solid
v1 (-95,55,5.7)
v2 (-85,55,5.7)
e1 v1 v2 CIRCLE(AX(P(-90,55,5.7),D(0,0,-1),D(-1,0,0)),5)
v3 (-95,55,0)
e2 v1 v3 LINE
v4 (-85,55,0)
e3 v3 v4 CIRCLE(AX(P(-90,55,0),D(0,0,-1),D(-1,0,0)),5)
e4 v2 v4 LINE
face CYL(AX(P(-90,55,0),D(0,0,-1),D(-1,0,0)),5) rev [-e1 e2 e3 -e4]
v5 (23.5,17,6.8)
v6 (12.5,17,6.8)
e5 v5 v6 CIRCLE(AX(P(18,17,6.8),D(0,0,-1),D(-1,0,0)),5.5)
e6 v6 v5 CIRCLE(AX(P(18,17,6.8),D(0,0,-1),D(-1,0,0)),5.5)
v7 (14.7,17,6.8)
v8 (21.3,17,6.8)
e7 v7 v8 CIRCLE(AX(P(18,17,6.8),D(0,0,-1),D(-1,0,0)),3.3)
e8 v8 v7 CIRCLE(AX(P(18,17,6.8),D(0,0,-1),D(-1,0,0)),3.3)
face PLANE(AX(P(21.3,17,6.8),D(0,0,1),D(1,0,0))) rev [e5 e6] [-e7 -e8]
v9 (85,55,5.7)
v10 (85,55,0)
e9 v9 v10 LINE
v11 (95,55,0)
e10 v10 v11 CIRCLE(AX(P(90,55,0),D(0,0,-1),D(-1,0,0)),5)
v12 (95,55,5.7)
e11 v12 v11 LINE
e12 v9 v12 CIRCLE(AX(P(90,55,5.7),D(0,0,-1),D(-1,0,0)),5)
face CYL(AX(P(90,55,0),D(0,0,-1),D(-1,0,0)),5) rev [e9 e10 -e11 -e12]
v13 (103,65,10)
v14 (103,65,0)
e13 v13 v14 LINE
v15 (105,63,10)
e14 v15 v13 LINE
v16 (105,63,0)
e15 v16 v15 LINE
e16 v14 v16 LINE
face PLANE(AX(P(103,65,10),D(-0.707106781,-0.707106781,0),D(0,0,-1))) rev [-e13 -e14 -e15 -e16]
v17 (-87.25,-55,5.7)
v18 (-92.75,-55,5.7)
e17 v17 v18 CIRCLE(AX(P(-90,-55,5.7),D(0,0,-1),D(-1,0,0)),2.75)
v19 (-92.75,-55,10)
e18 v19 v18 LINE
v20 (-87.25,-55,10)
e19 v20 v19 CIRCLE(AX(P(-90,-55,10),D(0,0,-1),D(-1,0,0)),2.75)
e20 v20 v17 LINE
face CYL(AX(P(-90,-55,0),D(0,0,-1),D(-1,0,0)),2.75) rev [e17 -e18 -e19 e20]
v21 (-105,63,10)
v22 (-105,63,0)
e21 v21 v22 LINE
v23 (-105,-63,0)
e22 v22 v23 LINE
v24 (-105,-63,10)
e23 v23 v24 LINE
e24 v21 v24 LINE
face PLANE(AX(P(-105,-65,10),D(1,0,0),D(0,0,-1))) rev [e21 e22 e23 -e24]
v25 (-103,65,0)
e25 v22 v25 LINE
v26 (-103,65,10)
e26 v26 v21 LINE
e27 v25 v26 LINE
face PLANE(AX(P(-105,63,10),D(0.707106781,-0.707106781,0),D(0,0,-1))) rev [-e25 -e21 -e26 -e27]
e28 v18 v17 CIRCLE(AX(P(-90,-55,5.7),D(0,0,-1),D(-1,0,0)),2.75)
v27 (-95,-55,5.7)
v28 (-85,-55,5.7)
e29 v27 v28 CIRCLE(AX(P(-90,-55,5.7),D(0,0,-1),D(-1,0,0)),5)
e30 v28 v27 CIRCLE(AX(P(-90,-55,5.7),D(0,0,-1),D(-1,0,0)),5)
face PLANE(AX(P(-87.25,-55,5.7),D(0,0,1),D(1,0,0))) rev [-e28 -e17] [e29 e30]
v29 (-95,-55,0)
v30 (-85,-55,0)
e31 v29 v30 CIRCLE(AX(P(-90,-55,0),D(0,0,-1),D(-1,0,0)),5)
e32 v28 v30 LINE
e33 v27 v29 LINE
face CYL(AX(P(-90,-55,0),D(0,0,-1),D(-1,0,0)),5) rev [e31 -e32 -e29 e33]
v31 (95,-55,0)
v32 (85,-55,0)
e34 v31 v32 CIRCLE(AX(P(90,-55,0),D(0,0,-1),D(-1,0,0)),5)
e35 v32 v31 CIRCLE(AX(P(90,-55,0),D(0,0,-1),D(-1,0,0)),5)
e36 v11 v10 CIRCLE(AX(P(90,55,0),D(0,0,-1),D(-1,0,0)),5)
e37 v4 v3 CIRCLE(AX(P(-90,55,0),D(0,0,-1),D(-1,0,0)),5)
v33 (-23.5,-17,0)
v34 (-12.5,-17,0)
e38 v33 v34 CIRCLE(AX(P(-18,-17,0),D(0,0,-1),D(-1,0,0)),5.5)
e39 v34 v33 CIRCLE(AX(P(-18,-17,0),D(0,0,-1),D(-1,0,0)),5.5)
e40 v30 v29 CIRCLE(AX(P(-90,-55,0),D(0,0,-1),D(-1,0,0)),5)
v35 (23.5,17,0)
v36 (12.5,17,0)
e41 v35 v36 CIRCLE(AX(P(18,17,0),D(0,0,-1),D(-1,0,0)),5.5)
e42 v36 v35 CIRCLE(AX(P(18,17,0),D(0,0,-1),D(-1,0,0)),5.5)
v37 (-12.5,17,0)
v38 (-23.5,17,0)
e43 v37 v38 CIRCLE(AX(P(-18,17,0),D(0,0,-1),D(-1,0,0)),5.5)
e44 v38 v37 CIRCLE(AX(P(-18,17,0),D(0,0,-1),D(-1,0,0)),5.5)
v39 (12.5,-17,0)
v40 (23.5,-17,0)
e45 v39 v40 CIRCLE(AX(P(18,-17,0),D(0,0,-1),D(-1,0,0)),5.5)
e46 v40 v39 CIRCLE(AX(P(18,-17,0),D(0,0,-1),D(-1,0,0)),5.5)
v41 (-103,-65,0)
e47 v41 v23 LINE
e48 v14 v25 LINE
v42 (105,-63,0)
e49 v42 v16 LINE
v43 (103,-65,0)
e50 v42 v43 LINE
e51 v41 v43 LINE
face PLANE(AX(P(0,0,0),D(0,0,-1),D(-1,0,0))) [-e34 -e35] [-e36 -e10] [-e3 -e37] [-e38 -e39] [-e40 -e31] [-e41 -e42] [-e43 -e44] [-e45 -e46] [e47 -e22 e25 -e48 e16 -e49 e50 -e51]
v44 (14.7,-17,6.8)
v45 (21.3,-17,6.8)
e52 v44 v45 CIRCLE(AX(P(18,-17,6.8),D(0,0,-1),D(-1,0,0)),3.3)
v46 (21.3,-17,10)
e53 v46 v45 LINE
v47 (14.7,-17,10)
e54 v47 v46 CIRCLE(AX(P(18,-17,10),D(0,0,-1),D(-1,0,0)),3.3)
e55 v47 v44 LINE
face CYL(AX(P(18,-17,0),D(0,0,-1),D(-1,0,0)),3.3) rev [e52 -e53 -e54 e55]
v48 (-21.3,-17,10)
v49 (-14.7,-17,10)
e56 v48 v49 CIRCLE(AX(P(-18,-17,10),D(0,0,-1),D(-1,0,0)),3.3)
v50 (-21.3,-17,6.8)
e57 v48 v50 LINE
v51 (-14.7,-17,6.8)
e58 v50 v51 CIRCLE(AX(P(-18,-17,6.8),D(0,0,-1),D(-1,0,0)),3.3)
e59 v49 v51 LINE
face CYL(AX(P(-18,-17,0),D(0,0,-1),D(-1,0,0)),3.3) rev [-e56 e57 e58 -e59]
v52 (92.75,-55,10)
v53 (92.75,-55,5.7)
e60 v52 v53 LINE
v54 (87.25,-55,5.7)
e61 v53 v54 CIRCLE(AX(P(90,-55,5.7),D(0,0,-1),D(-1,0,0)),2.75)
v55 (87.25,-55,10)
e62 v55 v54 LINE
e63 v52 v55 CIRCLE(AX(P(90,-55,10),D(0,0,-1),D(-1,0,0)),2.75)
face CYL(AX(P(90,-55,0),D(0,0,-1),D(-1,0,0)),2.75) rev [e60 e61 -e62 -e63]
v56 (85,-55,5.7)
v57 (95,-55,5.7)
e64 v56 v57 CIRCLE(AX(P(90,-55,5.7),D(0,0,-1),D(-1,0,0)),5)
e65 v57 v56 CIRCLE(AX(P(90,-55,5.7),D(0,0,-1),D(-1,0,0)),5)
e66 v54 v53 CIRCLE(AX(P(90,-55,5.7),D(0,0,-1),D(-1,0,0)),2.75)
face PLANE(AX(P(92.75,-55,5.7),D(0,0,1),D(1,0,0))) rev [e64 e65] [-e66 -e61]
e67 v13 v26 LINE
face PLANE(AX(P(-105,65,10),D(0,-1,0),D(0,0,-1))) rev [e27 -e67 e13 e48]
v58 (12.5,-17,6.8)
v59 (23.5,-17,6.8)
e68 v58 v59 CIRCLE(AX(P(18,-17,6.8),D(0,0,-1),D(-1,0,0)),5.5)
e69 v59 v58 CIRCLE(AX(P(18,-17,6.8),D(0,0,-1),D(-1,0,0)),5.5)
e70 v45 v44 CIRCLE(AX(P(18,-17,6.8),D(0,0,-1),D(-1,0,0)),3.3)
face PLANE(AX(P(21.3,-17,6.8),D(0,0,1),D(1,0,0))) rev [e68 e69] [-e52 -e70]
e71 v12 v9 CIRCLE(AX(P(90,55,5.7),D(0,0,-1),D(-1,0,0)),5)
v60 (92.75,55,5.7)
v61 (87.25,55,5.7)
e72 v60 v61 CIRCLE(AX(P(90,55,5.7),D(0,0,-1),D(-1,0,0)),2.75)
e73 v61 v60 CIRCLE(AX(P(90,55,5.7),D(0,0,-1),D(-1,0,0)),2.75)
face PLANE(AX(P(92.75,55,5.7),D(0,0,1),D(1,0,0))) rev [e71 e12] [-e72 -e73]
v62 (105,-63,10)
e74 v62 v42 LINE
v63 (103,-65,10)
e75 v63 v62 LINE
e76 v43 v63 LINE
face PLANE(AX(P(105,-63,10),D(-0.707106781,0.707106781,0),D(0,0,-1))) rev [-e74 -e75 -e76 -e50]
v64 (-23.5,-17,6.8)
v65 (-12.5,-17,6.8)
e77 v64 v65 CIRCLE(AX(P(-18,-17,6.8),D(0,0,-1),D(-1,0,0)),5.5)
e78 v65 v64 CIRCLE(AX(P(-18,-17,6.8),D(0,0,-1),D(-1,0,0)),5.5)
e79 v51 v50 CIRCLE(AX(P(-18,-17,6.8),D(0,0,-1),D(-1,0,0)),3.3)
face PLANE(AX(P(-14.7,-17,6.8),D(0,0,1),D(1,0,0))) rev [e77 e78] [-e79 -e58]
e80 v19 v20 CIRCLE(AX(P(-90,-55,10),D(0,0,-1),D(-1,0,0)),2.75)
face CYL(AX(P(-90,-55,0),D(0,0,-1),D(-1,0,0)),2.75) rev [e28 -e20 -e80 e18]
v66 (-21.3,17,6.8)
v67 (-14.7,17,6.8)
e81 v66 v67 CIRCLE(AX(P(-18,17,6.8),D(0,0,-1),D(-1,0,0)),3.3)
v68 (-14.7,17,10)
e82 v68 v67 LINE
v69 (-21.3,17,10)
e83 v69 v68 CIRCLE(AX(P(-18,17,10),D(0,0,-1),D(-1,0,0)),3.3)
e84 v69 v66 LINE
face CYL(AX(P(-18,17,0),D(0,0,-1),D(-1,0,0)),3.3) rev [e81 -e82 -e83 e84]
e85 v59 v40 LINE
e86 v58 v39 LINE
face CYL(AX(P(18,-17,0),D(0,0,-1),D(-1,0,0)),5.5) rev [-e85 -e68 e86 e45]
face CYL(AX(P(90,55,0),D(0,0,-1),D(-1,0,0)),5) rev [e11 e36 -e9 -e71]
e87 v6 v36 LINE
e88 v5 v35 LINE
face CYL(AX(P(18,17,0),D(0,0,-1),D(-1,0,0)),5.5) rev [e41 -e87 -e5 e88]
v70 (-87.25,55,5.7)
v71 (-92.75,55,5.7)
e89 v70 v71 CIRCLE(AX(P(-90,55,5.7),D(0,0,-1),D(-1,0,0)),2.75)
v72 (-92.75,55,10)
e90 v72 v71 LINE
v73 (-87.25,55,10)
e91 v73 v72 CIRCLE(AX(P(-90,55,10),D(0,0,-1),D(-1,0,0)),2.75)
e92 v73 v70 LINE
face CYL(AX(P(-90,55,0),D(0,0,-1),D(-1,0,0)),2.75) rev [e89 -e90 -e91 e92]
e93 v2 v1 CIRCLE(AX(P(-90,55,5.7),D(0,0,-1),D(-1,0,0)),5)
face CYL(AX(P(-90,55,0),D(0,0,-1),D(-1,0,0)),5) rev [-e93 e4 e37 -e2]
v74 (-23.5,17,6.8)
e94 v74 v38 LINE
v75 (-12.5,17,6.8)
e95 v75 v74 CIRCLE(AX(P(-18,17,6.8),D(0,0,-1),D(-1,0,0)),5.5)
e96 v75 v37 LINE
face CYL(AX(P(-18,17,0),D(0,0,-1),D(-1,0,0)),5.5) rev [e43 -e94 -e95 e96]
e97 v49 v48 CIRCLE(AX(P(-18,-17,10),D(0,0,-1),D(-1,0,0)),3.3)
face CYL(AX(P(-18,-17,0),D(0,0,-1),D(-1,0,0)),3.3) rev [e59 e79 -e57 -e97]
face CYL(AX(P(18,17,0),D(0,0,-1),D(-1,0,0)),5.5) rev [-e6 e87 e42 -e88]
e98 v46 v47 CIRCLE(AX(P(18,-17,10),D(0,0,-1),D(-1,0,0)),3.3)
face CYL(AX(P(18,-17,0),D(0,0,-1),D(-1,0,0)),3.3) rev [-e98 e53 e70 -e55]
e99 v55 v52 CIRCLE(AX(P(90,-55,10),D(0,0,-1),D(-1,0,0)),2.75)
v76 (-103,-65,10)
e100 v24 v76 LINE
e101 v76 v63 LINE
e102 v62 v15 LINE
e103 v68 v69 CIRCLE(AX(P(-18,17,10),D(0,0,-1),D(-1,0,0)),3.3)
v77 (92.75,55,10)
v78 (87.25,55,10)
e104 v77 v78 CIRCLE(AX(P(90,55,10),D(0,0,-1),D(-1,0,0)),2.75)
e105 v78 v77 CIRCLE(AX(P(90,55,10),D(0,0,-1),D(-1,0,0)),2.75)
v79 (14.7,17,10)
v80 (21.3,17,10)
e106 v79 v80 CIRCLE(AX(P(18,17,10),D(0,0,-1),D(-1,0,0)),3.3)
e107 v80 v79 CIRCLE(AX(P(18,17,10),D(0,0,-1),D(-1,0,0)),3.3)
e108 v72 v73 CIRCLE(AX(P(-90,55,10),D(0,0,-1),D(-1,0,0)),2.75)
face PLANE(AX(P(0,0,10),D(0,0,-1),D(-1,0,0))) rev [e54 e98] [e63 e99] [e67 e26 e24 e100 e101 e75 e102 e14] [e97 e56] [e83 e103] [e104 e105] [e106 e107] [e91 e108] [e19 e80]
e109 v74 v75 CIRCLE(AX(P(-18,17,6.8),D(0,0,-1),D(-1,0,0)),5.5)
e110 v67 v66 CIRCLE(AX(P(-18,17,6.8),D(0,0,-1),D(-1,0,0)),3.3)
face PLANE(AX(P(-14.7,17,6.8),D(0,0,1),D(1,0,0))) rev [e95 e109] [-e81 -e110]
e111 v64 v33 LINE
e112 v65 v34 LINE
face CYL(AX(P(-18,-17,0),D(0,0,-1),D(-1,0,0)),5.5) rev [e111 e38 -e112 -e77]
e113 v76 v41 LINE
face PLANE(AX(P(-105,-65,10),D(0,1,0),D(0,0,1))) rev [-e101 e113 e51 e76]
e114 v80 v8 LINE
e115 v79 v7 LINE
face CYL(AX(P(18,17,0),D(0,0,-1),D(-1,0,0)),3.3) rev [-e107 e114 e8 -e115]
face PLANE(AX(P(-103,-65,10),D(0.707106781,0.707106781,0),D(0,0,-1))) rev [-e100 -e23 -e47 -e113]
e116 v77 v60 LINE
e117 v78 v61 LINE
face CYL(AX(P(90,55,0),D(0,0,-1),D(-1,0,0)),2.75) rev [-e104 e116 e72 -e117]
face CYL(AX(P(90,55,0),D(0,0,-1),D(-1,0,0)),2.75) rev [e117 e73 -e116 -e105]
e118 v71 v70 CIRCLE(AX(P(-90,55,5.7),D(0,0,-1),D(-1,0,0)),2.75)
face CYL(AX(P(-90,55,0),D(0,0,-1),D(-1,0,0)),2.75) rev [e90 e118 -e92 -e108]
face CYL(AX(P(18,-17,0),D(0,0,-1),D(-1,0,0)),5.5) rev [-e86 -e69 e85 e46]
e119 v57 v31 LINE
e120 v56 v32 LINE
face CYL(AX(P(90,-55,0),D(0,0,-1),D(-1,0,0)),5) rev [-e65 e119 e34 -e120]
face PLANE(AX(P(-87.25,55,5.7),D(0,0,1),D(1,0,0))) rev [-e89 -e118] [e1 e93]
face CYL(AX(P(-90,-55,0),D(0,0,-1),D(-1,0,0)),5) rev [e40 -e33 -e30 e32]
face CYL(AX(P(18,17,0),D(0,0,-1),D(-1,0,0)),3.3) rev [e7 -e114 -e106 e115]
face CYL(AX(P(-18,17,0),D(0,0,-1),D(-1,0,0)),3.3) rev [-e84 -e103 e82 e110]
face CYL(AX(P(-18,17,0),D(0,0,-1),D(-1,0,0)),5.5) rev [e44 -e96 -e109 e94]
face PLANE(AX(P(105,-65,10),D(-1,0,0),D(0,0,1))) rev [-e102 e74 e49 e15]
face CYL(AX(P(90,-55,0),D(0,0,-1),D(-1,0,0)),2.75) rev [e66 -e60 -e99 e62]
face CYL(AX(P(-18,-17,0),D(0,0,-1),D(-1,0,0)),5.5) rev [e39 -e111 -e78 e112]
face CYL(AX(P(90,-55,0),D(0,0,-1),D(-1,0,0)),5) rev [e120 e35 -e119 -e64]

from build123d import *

# Parameters (mm, degrees)
SKETCH1_W                                           = 210
SKETCH1_H                                           = 130
BOSS_EXTRUDE1_DEPTH                                 = 10
HOLE_SIZE_PER_SOCKET_HEAD_CAP_SCREW_TYP_D           = 6.6
HOLE_SIZE_PER_SOCKET_HEAD_CAP_SCREW_TYP_CBORE_D     = 11
HOLE_SIZE_PER_SOCKET_HEAD_CAP_SCREW_TYP_CBORE_DEPTH = 6.8
HOLE_SIZE_PER_SOCKET_HEAD_CAP_SCREW_2_D             = 5.5
HOLE_SIZE_PER_SOCKET_HEAD_CAP_SCREW_2_CBORE_D       = 10
HOLE_SIZE_PER_SOCKET_HEAD_CAP_SCREW_2_CBORE_DEPTH   = 5.7
CHAMFER1_SIZE                                       = 2


with BuildPart() as part:
    # Sketch1 → Boss-Extrude1 (new body)
    with BuildSketch(Plane.XY):
        Rectangle(SKETCH1_W, SKETCH1_H)
    extrude(amount=BOSS_EXTRUDE1_DEPTH)

    # Hole size _per socket head cap screw typ (through all)
    with Locations(Plane(origin=(-18, -17, 0), x_dir=(-1, 0, 0), z_dir=(0, 0, -1))):
        with Locations((0, 0), (-36, 0), (-36, 34), (0, 34)):
            CounterBoreHole(HOLE_SIZE_PER_SOCKET_HEAD_CAP_SCREW_TYP_D / 2, HOLE_SIZE_PER_SOCKET_HEAD_CAP_SCREW_TYP_CBORE_D / 2, HOLE_SIZE_PER_SOCKET_HEAD_CAP_SCREW_TYP_CBORE_DEPTH)

    # Hole size _per socket head cap screw 2 (through all)
    with Locations(Plane(origin=(-90, -55, 0), x_dir=(-1, 0, 0), z_dir=(0, 0, -1))):
        with Locations((0, 0), (0, 110), (-180, 110), (-180, 0)):
            CounterBoreHole(HOLE_SIZE_PER_SOCKET_HEAD_CAP_SCREW_2_D / 2, HOLE_SIZE_PER_SOCKET_HEAD_CAP_SCREW_2_CBORE_D / 2, HOLE_SIZE_PER_SOCKET_HEAD_CAP_SCREW_2_CBORE_DEPTH)

    # Chamfer1
    chamfer1_edges = [part.edges().sort_by_distance(p)[0] for p in [
        (105, -65, 5),
        (-105, -65, 5),
        (-105, 65, 5),
        (105, 65, 5),
    ]]
    chamfer(chamfer1_edges, length=CHAMFER1_SIZE)


solid = part.part
